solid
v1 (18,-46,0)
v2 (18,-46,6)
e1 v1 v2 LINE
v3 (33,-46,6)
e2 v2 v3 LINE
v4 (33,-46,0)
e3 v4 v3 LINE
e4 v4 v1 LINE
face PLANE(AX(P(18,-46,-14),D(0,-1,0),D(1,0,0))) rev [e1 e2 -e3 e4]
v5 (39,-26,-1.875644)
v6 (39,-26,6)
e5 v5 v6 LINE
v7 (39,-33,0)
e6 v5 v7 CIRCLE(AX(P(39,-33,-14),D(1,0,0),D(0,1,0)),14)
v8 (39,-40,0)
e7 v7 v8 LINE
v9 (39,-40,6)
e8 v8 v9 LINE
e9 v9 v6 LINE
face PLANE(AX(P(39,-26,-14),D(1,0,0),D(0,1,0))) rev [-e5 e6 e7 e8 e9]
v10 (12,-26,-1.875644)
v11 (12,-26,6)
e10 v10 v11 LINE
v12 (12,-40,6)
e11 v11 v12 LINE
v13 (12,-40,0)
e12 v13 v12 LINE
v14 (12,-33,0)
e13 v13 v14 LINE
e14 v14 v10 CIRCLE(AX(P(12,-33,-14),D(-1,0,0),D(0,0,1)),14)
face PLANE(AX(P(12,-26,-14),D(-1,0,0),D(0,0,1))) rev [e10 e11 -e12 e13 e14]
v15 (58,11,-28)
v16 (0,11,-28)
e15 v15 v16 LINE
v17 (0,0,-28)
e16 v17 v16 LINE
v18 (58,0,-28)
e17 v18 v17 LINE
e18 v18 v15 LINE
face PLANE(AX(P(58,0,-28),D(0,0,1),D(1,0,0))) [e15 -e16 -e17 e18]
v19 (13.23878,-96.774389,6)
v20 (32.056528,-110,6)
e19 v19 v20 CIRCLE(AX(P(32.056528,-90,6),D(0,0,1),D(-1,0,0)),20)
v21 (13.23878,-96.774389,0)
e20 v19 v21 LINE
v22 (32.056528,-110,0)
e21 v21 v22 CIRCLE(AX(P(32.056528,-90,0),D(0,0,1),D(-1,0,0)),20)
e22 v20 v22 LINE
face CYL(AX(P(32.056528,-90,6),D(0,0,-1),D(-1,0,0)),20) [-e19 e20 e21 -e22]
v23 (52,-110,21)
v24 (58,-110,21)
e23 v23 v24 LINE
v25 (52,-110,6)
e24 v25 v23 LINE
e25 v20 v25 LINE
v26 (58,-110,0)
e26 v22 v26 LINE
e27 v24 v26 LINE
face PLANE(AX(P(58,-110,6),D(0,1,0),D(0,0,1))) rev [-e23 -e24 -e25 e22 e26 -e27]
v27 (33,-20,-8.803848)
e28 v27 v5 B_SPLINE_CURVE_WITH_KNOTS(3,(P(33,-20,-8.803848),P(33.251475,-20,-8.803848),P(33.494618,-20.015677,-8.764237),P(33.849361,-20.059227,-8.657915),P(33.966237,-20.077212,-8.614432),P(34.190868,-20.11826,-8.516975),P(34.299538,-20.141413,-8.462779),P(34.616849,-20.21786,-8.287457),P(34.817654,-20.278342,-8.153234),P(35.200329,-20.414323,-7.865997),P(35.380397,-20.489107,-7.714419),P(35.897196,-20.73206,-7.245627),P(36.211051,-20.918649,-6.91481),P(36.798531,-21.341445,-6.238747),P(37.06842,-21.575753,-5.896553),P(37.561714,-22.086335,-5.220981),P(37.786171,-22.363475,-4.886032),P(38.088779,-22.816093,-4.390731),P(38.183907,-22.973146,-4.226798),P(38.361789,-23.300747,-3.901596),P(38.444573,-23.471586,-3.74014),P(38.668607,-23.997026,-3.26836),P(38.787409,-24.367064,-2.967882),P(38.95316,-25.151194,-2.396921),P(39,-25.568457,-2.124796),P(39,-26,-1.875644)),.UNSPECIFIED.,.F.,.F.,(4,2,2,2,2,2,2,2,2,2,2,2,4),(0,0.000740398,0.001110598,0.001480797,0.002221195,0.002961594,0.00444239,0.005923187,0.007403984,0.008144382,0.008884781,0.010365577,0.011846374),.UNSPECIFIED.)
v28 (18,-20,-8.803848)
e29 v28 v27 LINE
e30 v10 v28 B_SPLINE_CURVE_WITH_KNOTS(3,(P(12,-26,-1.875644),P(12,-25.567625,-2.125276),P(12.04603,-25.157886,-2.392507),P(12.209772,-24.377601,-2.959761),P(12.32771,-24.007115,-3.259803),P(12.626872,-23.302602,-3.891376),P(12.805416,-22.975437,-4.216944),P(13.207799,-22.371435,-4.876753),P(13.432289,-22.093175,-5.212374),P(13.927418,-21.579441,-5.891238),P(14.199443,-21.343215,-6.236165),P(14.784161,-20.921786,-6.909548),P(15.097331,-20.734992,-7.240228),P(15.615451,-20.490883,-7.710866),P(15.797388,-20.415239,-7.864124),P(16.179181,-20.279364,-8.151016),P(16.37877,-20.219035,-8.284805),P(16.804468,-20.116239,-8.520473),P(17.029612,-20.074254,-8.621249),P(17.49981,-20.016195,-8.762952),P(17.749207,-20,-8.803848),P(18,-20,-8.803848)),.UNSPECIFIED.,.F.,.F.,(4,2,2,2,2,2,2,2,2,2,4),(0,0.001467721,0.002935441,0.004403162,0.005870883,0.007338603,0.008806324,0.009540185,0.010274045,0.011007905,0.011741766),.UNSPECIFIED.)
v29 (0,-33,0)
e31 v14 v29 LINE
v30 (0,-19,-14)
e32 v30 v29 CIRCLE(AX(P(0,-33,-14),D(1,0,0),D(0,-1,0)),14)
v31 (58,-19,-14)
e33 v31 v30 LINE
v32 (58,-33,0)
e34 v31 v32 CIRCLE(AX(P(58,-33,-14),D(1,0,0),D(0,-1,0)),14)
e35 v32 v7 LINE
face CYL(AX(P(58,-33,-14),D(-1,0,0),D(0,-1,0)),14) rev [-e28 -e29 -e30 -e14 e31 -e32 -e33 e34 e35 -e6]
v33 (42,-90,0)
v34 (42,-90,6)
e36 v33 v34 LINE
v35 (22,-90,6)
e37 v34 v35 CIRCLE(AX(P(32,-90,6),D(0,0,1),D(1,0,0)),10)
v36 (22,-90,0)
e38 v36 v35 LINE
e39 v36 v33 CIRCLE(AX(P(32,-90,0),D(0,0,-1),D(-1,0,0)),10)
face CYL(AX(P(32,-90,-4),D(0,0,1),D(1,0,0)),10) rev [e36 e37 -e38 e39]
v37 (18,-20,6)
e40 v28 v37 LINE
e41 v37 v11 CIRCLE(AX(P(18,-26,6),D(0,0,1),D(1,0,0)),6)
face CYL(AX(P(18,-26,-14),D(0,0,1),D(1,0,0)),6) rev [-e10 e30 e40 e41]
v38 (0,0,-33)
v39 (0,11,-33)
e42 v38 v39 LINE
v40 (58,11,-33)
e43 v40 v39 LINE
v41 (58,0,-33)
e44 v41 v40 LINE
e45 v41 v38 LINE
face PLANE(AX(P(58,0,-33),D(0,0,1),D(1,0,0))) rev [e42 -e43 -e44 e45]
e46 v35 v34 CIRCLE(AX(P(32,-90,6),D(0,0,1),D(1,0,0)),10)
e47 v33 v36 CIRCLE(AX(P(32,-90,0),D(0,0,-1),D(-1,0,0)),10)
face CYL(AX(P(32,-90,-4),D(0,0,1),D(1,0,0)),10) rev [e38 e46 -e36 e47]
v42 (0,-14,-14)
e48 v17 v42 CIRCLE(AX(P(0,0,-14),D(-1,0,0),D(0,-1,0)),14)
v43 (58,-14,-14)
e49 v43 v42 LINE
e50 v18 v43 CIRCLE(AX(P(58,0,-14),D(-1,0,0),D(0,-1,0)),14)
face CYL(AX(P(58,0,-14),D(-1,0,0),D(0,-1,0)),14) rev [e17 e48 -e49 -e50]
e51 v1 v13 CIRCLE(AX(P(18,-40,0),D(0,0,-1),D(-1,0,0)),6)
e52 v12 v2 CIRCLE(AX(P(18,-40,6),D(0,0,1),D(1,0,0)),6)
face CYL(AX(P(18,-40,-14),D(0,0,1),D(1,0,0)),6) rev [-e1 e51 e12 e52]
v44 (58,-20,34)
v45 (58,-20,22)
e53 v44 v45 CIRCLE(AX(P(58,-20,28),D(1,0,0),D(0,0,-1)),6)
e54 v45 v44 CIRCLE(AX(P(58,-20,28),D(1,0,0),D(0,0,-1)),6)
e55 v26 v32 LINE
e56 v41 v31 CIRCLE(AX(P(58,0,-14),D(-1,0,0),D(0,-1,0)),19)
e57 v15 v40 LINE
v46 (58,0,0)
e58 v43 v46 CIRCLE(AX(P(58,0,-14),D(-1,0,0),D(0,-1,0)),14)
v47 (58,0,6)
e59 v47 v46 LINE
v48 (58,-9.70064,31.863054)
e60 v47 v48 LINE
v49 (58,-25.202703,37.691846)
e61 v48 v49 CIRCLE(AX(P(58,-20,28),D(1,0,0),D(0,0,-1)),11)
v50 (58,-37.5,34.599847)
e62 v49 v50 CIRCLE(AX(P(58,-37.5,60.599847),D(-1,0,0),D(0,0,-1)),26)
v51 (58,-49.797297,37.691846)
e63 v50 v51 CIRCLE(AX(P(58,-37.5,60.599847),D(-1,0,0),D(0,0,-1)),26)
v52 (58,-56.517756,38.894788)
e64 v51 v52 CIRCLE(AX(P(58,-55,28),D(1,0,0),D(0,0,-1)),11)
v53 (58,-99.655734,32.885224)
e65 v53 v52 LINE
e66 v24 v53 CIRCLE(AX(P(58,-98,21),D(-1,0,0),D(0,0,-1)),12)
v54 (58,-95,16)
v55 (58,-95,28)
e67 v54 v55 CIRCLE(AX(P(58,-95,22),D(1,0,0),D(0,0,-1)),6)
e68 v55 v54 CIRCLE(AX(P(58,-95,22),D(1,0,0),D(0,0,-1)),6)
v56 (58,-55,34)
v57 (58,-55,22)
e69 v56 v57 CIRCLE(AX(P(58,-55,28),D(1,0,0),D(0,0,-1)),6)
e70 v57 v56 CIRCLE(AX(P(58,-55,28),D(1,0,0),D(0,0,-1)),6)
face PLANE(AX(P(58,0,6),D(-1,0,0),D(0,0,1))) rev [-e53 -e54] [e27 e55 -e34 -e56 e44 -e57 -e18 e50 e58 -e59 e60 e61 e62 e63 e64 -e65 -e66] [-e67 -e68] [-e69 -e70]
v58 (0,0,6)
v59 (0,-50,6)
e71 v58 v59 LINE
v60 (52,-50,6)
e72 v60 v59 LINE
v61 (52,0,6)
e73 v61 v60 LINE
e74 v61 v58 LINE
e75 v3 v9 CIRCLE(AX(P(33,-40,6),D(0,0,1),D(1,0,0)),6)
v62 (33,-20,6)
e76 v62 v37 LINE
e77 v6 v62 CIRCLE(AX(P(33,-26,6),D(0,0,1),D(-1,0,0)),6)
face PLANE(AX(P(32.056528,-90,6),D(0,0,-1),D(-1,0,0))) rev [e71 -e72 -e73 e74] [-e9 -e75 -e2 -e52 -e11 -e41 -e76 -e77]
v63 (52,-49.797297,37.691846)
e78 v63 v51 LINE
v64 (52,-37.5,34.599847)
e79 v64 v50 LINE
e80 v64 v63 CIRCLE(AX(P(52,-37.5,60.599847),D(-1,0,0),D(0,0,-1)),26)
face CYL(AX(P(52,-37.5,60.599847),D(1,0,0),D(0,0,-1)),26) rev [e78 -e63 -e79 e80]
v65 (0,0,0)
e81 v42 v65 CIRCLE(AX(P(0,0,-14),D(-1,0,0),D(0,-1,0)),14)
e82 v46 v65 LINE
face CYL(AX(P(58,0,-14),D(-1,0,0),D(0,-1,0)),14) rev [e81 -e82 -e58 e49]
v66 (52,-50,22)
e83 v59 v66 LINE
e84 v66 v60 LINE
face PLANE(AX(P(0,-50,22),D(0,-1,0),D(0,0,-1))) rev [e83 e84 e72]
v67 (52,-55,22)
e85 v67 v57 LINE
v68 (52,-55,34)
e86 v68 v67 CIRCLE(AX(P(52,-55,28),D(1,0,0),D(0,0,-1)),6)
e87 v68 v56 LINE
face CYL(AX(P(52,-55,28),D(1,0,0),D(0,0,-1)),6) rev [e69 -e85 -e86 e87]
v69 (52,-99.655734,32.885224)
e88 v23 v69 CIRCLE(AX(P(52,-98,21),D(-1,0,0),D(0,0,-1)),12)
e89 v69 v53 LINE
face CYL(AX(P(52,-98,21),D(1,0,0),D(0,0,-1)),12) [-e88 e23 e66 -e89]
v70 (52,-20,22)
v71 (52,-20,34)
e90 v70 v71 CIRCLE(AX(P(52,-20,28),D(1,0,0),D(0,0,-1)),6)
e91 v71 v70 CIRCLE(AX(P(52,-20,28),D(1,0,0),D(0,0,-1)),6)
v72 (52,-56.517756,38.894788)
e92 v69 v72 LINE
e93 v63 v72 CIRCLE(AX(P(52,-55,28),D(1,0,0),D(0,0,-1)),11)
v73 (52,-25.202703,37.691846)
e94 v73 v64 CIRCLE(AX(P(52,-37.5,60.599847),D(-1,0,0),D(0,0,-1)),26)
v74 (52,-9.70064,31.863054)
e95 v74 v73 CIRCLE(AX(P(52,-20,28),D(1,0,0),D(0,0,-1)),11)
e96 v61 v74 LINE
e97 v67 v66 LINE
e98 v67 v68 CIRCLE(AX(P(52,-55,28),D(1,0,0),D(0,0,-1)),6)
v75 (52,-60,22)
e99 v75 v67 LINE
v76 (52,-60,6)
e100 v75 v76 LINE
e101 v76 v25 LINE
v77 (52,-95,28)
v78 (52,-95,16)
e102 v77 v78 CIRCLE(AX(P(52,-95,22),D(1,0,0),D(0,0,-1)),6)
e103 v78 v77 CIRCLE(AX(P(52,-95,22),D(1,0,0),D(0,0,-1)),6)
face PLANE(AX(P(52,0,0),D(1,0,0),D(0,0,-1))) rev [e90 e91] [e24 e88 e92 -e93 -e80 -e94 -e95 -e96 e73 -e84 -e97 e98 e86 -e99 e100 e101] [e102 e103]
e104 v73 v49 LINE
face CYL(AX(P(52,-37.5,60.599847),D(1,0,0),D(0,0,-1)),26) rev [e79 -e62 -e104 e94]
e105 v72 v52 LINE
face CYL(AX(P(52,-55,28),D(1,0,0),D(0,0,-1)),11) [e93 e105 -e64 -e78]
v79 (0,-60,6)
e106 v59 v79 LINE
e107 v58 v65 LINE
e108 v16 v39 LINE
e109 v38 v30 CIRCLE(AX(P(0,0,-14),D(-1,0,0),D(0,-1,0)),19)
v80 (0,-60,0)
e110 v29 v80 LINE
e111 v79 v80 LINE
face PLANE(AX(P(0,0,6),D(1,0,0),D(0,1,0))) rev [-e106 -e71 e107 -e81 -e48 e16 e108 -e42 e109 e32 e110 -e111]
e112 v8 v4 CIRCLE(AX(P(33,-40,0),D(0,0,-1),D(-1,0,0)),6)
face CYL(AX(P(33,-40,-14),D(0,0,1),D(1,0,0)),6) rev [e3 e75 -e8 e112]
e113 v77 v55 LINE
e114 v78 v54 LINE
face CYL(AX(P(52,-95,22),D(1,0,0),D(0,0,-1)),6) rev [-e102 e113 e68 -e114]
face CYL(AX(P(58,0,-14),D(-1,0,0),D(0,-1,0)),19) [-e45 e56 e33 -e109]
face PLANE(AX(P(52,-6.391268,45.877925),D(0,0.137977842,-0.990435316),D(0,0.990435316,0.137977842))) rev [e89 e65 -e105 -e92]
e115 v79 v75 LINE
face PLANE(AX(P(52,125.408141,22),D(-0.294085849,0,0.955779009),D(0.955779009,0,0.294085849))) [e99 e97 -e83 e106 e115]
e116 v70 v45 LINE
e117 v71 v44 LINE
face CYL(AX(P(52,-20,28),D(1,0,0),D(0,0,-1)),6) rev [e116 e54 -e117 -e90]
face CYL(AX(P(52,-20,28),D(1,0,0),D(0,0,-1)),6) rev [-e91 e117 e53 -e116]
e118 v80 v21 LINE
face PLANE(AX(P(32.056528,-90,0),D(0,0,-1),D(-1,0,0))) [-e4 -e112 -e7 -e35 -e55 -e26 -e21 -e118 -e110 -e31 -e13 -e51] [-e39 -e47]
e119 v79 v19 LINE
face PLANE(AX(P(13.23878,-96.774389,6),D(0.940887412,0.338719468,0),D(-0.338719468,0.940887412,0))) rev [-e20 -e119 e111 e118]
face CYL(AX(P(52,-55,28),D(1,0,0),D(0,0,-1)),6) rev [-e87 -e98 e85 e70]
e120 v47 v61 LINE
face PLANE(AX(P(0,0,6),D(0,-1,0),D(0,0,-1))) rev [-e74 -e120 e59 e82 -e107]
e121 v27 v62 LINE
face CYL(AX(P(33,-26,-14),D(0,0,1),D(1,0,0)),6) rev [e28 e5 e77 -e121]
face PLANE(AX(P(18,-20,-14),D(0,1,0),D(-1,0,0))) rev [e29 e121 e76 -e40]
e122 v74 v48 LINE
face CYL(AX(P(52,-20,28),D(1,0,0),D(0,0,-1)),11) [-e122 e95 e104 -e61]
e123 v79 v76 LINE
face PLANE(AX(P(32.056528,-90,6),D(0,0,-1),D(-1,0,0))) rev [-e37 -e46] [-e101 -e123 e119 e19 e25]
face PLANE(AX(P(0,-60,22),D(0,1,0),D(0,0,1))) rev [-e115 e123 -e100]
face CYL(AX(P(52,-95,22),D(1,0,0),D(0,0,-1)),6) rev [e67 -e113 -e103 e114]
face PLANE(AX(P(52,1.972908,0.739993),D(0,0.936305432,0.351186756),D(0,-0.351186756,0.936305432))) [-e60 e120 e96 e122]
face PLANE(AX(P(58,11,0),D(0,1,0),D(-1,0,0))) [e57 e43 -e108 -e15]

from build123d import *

# Parameters (mm, degrees)
WALL_PLATE_DEPTH           = 6
SIDE_WEB_SKETCH_R          = 6
SIDE_WEB_DEPTH             = 6
CLAMP_BLOCK_SKETCH_W       = 52
CLAMP_BLOCK_SKETCH_H       = 10
CLAMP_BLOCK_DEPTH          = 16
CLAMP_BLOCK_CUT_DEPTH      = 93.11405973
CLAMP_BLOCK_CUT_DEPTH_BACK = 16
U_SADDLE_DEPTH             = 58
LIGHTENING_WINDOW_DEPTH    = 20
HOLE_SKETCH_R              = 10
HOLE_CUT_DEPTH             = 10


with BuildPart() as part:
    # Wall Plate Sketch → Wall Plate (new body)
    with BuildSketch(Plane.XY):
        with BuildLine():
            Line((0, 0), (0, -60))
            Line((0, -60), (13.238780172, -96.774389365))
            ThreePointArc((13.238780172, -96.774389365), (20.556262919, -106.362881582), (32.056528409, -110))
            Line((32.056528409, -110), (38, -110))
            Line((38, -110), (58, -110))
            Line((58, -110), (58, 0))
            Line((58, 0), (0, 0))
        make_face()
    extrude(amount=WALL_PLATE_DEPTH)

    # Side Web Sketch → Side Web (add)
    with BuildSketch(Plane(origin=(58, 0, 0), x_dir=(0, 0, -1), z_dir=(1, 0, 0))):
        with BuildLine():
            ThreePointArc((-21, -110), (-28.878172083, -107.051762515), (-32.885223791, -99.655734106))
            Line((-32.885223791, -99.655734106), (-38.894788475, -56.517756263))
            ThreePointArc((-38.894788475, -56.517756263), (-38.82790492, -53.0618372), (-37.691846294, -49.797297297))
            ThreePointArc((-37.691846294, -49.797297297), (-34.599846625, -37.5), (-37.691846294, -25.202702703))
            ThreePointArc((-37.691846294, -25.202702703), (-38.296228327, -16.128607197), (-31.863054321, -9.700640247))
            Line((-31.863054321, -9.700640247), (-6, 0))
            Line((-6, 0), (-6, -110))
            Line((-6, -110), (-21, -110))
        make_face()
        with Locations((-22, -95)):
            Circle(SIDE_WEB_SKETCH_R, mode=Mode.SUBTRACT)
        with Locations((-28, -55)):
            Circle(SIDE_WEB_SKETCH_R, mode=Mode.SUBTRACT)
        with Locations((-28, -20)):
            Circle(SIDE_WEB_SKETCH_R, mode=Mode.SUBTRACT)
    extrude(amount=-SIDE_WEB_DEPTH)

    # Clamp Block Sketch → Clamp Block (add)
    with BuildSketch(Plane.XY.offset(6)):
        with Locations((26, -55)):
            Rectangle(CLAMP_BLOCK_SKETCH_W, CLAMP_BLOCK_SKETCH_H)
    extrude(amount=CLAMP_BLOCK_DEPTH)

    # Clamp Block Cut Sketch → Clamp Block Cut (cut, two sides: drawn at the far end of the back side and taken through both)
    with BuildSketch(Plane(origin=(0, -50, 0), x_dir=(1, 0, 0), z_dir=(0, 1, 0)).offset(-CLAMP_BLOCK_CUT_DEPTH_BACK)):
        Polygon((0, -22), (52, -22), (0, -6), align=None)
    extrude(amount=CLAMP_BLOCK_CUT_DEPTH + CLAMP_BLOCK_CUT_DEPTH_BACK, mode=Mode.SUBTRACT)

    # U Saddle Sketch → U Saddle (add)
    with BuildSketch(Plane.ZY):
        with BuildLine():
            Line((0, -33), (0, 0))
            ThreePointArc((0, 0), (-14, -14), (-28, 0))
            Line((-28, 0), (-28, 11))
            Line((-28, 11), (-33, 11))
            Line((-33, 11), (-33, 0))
            ThreePointArc((-33, 0), (-27.435028843, -13.435028843), (-14, -19))
            ThreePointArc((-14, -19), (-4.100505063, -23.100505063), (0, -33))
        make_face()
    extrude(amount=-U_SADDLE_DEPTH)

    # Lightening Window Sketch → Lightening Window (cut)
    with BuildSketch(Plane.XY.offset(6)):
        with BuildLine():
            Line((18, -20), (33, -20))
            ThreePointArc((33, -20), (37.242640687, -21.757359313), (39, -26))
            Line((39, -26), (39, -40))
            ThreePointArc((39, -40), (37.242640687, -44.242640687), (33, -46))
            Line((33, -46), (18, -46))
            ThreePointArc((18, -46), (13.757359313, -44.242640687), (12, -40))
            Line((12, -40), (12, -26))
            ThreePointArc((12, -26), (13.757359313, -21.757359313), (18, -20))
        make_face()
    extrude(amount=-LIGHTENING_WINDOW_DEPTH, mode=Mode.SUBTRACT)

    # Hole Sketch → Hole Cut (cut)
    with BuildSketch(Plane.XY.offset(6)):
        with Locations((32, -90)):
            Circle(HOLE_SKETCH_R)
    extrude(amount=-HOLE_CUT_DEPTH, mode=Mode.SUBTRACT)


solid = part.part
